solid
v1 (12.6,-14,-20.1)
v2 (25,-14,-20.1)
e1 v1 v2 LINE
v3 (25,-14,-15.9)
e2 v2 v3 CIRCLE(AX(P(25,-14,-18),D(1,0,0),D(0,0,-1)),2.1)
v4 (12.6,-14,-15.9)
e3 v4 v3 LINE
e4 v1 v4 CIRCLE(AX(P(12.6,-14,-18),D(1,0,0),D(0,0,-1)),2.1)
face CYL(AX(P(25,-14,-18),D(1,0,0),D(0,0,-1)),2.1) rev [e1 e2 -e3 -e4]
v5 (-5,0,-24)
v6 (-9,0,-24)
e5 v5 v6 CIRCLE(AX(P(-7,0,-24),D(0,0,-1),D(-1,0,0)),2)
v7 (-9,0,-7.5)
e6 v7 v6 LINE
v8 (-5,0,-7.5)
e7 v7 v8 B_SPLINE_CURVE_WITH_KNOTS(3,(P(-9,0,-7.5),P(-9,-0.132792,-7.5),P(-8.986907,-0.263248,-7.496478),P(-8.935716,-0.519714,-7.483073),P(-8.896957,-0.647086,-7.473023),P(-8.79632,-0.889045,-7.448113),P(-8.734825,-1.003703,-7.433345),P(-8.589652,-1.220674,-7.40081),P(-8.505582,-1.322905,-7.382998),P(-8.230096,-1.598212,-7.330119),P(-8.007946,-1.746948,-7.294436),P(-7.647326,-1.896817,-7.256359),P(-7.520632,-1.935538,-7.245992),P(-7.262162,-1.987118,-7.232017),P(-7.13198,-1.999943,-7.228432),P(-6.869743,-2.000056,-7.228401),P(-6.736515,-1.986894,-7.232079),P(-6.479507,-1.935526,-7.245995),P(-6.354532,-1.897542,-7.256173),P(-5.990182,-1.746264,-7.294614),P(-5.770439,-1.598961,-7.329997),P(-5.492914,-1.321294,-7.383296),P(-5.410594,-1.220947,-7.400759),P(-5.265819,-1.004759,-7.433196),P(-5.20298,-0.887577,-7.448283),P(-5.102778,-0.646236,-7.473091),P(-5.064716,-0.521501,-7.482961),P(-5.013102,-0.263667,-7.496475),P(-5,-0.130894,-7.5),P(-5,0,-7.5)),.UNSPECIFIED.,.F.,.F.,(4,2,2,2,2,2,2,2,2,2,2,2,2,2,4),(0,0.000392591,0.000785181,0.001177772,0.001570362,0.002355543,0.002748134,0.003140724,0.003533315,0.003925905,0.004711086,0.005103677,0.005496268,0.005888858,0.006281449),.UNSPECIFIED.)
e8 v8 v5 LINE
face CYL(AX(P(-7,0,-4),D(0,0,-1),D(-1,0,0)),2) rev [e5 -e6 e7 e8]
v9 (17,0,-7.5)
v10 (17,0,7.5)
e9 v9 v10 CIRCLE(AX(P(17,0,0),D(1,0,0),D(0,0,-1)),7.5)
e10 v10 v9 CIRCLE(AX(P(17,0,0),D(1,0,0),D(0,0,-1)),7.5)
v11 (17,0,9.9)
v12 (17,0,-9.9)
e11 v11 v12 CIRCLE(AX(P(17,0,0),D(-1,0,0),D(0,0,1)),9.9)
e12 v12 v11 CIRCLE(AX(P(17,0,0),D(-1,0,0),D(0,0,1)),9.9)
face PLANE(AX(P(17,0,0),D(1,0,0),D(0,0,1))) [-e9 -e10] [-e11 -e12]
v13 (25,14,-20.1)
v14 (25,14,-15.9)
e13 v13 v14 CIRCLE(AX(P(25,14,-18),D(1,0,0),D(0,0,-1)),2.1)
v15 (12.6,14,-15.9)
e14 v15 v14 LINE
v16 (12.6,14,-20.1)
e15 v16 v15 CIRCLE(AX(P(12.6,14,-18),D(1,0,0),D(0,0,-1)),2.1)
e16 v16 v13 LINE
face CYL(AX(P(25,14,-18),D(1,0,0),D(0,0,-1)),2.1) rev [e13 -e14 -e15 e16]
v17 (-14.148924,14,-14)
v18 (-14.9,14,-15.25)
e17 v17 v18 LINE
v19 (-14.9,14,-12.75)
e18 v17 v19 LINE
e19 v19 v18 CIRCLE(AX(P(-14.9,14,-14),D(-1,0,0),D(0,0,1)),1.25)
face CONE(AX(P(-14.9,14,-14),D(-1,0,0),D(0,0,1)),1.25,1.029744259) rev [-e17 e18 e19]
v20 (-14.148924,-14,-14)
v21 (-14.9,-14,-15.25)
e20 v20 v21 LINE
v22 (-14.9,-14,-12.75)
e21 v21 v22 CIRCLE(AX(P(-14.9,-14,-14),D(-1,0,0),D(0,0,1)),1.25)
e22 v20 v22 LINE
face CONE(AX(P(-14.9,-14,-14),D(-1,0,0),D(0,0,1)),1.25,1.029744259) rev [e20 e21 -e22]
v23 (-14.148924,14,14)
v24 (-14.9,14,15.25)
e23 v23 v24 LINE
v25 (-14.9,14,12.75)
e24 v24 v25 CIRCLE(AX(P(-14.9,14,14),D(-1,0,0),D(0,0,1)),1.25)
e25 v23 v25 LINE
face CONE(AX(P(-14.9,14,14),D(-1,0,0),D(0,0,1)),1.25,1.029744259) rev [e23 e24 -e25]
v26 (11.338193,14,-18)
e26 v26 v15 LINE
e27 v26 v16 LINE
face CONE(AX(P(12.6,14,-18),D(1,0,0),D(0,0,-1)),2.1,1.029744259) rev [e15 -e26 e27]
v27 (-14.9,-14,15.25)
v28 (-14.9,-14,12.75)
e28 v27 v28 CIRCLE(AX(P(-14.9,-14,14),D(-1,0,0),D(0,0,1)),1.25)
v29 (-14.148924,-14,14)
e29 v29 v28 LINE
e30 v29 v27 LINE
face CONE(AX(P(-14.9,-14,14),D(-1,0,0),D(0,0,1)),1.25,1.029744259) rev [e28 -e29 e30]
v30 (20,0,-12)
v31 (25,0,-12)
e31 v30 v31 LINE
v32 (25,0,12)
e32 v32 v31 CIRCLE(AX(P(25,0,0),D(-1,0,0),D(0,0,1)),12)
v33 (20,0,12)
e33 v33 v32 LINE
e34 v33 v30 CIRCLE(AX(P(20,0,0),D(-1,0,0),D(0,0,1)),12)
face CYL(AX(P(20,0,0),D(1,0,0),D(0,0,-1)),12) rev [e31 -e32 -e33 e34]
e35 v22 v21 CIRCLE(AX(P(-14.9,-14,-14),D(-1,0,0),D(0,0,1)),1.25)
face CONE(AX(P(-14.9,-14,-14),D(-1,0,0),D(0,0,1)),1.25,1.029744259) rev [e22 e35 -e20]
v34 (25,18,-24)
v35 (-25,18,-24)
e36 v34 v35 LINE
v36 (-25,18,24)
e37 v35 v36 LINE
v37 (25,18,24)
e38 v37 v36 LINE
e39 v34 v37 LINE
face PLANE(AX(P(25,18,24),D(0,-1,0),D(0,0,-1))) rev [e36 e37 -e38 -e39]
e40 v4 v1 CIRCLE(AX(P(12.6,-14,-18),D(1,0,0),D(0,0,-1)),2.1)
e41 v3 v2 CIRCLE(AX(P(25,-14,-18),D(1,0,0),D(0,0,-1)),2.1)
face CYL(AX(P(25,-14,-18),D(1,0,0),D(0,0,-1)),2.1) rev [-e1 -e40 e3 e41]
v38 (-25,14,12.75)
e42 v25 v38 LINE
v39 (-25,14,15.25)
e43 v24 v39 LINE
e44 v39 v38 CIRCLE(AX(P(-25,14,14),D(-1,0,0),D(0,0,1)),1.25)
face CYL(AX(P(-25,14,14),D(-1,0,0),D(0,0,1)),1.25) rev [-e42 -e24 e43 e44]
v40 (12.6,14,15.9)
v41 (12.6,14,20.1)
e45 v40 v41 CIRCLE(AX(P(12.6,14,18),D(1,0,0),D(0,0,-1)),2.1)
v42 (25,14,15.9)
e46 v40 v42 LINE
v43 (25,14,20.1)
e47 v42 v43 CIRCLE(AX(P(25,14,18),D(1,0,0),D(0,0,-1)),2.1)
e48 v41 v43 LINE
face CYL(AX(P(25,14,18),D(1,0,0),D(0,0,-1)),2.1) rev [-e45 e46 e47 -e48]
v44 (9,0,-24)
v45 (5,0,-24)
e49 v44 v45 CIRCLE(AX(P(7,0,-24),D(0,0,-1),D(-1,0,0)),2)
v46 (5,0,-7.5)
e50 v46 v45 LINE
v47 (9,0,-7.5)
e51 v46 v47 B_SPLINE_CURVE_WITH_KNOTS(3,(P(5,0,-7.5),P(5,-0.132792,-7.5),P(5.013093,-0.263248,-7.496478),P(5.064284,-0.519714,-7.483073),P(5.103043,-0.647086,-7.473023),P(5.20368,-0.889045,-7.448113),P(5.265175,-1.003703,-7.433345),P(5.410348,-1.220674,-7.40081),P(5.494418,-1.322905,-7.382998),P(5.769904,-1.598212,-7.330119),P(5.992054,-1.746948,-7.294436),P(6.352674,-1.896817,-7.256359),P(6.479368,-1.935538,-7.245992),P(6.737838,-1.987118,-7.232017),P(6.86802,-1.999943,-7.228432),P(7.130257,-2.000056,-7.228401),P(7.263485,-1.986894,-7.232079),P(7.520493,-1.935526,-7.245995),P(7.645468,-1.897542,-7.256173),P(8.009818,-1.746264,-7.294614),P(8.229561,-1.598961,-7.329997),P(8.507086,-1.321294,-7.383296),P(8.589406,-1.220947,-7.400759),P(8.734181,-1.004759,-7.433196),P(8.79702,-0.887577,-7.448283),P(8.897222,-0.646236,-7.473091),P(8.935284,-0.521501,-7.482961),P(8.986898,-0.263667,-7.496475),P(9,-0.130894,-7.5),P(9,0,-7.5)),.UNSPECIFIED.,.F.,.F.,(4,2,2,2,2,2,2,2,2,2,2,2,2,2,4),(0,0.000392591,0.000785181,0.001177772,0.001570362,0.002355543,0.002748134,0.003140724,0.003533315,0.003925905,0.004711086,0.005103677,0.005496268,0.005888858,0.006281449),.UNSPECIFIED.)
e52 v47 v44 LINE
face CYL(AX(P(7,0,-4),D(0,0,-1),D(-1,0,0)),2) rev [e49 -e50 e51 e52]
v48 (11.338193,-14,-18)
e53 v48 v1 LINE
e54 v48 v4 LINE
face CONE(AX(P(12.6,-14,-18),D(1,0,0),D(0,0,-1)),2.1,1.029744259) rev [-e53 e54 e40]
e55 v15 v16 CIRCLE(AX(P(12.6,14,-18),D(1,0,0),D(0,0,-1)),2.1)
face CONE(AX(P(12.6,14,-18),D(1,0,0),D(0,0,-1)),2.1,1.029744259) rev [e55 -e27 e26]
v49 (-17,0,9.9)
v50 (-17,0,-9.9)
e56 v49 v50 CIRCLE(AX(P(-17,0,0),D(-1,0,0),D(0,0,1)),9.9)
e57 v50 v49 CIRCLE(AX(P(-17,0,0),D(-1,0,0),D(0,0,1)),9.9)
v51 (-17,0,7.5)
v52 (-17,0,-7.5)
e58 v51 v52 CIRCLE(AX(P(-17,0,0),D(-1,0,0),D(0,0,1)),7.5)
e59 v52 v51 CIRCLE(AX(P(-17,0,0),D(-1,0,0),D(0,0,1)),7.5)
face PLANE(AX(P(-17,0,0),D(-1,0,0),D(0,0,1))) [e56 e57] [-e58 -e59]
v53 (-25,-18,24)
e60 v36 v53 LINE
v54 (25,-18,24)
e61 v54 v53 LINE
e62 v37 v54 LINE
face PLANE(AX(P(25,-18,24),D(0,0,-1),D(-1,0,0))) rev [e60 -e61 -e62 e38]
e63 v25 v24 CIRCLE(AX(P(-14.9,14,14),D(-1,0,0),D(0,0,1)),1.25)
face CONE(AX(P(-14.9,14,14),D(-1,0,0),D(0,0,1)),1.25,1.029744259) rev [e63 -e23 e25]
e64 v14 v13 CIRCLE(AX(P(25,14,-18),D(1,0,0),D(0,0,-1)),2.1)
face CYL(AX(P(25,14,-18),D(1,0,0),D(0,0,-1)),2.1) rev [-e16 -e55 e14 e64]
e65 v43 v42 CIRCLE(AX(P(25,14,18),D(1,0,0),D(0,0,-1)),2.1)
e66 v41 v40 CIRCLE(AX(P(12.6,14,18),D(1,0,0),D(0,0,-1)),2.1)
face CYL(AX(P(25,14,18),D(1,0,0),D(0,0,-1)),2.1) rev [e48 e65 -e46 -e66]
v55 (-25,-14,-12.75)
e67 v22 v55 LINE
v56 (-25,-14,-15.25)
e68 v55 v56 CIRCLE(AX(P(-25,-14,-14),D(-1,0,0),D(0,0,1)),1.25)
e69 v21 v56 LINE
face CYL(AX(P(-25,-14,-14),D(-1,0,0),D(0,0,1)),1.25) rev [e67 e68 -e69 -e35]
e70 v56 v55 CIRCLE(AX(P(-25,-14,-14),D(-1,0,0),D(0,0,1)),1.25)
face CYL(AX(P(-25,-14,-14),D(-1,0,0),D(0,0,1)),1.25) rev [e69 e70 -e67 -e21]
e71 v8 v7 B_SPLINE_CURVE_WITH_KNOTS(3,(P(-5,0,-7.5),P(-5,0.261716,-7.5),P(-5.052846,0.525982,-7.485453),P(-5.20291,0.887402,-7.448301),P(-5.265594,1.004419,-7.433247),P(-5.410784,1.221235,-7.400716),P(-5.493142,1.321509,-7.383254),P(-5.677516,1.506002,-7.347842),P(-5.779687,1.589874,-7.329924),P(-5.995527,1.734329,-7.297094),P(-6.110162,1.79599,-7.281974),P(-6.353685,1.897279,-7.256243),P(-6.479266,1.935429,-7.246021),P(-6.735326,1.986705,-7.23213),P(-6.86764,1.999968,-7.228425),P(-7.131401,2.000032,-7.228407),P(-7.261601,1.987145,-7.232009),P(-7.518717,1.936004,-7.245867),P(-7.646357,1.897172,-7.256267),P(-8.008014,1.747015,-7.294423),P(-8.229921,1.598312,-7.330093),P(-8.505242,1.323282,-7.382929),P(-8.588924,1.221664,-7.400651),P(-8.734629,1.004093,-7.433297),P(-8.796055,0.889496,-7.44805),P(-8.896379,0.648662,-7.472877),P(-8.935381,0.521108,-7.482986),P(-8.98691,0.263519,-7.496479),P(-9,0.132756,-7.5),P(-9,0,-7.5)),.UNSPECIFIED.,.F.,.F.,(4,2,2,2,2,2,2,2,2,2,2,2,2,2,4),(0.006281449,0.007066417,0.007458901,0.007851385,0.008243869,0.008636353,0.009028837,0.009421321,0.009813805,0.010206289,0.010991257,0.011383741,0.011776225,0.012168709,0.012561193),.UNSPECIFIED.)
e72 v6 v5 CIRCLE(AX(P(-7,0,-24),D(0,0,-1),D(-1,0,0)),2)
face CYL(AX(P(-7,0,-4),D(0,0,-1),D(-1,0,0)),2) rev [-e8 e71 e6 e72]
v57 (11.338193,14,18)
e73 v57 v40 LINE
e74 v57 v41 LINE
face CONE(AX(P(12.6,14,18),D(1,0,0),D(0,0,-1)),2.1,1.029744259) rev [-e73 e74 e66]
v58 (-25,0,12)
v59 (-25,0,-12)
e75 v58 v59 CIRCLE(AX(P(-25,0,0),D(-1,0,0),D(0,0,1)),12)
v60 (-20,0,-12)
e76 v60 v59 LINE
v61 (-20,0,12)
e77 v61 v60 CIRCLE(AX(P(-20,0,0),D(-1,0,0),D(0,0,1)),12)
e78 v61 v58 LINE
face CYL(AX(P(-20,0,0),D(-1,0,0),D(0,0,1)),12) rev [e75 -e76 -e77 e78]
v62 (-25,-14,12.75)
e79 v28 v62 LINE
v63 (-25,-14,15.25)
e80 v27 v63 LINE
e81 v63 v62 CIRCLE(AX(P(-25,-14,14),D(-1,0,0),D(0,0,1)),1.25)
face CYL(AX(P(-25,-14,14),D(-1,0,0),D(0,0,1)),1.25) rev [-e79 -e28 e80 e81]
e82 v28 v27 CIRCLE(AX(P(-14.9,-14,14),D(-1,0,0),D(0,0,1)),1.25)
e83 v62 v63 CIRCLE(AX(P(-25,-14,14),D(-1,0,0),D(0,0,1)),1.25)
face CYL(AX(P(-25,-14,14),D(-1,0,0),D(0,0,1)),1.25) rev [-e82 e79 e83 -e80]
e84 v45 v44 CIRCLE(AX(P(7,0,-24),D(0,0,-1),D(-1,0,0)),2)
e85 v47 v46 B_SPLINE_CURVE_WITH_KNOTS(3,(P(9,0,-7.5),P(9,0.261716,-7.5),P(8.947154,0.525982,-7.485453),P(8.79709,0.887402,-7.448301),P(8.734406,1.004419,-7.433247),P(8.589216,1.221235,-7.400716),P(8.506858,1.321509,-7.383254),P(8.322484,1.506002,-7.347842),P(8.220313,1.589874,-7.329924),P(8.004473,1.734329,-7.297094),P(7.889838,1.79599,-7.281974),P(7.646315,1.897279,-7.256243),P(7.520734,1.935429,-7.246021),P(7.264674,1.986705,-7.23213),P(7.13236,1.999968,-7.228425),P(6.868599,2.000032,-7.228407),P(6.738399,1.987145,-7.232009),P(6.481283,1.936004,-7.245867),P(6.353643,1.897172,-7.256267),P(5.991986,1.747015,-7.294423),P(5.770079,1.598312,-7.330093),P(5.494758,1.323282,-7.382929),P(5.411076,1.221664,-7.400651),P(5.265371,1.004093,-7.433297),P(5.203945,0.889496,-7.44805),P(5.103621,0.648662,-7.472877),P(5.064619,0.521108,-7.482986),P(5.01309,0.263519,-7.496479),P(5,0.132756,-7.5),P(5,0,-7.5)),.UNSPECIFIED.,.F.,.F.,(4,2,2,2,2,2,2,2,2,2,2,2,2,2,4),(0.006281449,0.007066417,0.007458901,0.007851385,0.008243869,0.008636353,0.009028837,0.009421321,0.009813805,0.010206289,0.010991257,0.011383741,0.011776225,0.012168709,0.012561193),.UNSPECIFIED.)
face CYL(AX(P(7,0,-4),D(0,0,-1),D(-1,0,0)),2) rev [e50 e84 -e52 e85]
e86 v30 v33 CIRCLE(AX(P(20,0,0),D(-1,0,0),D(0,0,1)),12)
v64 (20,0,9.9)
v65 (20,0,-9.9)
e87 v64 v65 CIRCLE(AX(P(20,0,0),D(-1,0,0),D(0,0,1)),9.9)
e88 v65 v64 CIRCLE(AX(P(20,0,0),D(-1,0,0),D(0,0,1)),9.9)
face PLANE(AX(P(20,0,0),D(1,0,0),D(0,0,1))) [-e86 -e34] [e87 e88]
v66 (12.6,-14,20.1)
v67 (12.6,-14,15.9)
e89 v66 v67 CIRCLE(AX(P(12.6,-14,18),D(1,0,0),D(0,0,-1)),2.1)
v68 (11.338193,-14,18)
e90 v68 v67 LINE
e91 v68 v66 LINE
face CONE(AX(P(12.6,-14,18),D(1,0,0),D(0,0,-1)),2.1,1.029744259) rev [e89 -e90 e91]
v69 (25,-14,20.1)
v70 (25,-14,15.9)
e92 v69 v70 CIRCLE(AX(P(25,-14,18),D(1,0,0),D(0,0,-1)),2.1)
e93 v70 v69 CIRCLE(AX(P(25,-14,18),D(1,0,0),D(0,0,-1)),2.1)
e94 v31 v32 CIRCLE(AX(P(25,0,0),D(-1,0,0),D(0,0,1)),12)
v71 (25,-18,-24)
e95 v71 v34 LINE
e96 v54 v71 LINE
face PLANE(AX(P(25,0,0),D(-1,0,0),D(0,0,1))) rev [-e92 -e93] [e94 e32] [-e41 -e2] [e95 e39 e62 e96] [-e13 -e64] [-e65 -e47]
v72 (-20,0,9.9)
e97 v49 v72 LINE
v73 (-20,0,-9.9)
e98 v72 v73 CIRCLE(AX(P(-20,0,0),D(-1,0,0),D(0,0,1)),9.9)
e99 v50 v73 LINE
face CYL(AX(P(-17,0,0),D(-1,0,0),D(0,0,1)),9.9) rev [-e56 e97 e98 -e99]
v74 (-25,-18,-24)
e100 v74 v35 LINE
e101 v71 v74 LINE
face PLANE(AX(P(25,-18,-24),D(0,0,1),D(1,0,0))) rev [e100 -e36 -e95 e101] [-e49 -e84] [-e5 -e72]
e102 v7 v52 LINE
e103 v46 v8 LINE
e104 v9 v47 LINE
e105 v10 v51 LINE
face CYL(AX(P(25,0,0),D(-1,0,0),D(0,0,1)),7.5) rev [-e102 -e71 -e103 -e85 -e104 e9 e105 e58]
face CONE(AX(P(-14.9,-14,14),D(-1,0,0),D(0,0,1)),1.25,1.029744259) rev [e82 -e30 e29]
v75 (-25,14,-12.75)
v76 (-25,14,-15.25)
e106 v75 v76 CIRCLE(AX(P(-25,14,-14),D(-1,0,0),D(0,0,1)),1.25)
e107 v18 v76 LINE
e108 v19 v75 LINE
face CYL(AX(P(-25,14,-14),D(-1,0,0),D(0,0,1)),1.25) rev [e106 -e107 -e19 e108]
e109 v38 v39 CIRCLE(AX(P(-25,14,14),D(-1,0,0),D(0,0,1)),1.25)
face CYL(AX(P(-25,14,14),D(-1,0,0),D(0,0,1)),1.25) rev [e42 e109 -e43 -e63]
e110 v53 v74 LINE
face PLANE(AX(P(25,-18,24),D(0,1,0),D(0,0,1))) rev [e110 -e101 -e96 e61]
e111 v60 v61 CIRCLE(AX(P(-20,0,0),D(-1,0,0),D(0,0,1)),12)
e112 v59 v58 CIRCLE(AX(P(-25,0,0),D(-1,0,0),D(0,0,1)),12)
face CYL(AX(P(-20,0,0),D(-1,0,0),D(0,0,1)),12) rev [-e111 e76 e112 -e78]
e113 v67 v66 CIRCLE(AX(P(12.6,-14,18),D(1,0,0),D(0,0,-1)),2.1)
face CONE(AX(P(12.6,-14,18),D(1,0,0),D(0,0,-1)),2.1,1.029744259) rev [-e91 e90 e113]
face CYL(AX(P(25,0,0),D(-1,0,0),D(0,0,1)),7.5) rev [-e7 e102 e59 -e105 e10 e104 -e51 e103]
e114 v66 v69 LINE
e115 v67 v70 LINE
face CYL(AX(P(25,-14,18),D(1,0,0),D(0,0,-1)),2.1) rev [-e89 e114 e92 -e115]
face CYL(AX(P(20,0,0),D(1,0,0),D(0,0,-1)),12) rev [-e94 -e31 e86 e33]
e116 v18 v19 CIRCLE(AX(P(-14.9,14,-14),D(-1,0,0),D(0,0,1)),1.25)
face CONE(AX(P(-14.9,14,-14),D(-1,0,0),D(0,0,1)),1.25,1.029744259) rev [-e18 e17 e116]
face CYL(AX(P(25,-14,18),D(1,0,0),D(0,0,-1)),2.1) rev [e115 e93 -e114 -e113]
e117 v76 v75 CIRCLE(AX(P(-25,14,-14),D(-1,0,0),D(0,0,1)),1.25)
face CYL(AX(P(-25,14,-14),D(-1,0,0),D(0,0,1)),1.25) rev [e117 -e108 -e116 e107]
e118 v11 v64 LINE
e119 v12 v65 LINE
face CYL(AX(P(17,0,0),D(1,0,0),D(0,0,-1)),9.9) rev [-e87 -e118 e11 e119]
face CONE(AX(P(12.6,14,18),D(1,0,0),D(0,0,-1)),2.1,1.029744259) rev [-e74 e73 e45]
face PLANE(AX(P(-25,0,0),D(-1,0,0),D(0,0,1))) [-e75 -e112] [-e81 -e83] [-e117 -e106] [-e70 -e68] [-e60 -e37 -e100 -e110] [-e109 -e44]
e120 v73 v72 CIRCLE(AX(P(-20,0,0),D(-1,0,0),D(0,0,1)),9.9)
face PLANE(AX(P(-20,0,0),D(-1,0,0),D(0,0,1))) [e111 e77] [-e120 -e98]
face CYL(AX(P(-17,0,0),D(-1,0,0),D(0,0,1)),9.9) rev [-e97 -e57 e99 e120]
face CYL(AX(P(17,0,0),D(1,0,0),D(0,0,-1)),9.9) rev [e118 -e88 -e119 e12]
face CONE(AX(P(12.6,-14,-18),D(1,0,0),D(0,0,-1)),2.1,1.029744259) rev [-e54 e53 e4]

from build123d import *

# Parameters (mm, degrees)
SKETCH1_W             = 48
SKETCH1_H             = 36
SKETCH1_R             = 7.5
BOSS_EXTRUDE1_DEPTH   = 25
SKETCH2_R             = 12
CUT_EXTRUDE1_DEPTH    = 5
SKETCH3_R             = 9.9
CUT_EXTRUDE2_DEPTH    = 3
SKETCH5_R             = 2
CUT_EXTRUDE3_DEPTH    = 20
M5_TAPPED_HOLE1_D     = 4.2
M5_TAPPED_HOLE1_DEPTH = 12.4
M5_TAPPED_HOLE1_TIP   = 1.2618073
M3_TAPPED_HOLE1_D     = 2.5
M3_TAPPED_HOLE1_DEPTH = 10.1
M3_TAPPED_HOLE1_TIP   = 0.751075774


with BuildPart() as part:
    # Sketch1 → Boss-Extrude1 (new, symmetric)
    with BuildSketch(Plane(origin=(0, 0, 0), x_dir=(0, 0, -1), z_dir=(1, 0, 0))):
        Rectangle(SKETCH1_W, SKETCH1_H)
        Circle(SKETCH1_R, mode=Mode.SUBTRACT)
    extrude(amount=BOSS_EXTRUDE1_DEPTH, both=True)

    # Sketch2 → Cut-Extrude1 (cut)
    with BuildSketch(Plane.ZY.offset(25)):
        Circle(SKETCH2_R)
    cut_extrude1 = extrude(amount=-CUT_EXTRUDE1_DEPTH, mode=Mode.SUBTRACT)

    # Sketch3 → Cut-Extrude2 (cut)
    with BuildSketch(Plane.ZY.offset(20)):
        Circle(SKETCH3_R)
    cut_extrude2 = extrude(amount=-CUT_EXTRUDE2_DEPTH, mode=Mode.SUBTRACT)

    # Mirror4: Cut-Extrude1, Cut-Extrude2 across plane
    add(cut_extrude1.mirror(Plane(origin=(0, 0, 0), x_dir=(0, 0, 1), z_dir=(1, 0, 0))), mode=Mode.SUBTRACT)
    add(cut_extrude2.mirror(Plane(origin=(0, 0, 0), x_dir=(0, 0, 1), z_dir=(1, 0, 0))), mode=Mode.SUBTRACT)

    # Sketch5 → Cut-Extrude3 (cut)
    with BuildSketch(Plane(origin=(0, 0, -24), x_dir=(-1, 0, 0), z_dir=(0, 0, -1))):
        with Locations((7, 0)):
            Circle(SKETCH5_R)
        with Locations((-7, 0)):
            Circle(SKETCH5_R)
    extrude(amount=-CUT_EXTRUDE3_DEPTH, mode=Mode.SUBTRACT)

    # M5 Tapped Hole1
    with Locations(Plane(origin=(25, 0, 0), x_dir=(0, 0, -1), z_dir=(1, 0, 0))):
        with Locations((-18, 14), (18, 14), (-18, -14), (18, -14)):
            Hole(M5_TAPPED_HOLE1_D / 2, depth=M5_TAPPED_HOLE1_DEPTH)
            with Locations((0, 0, -(M5_TAPPED_HOLE1_DEPTH + M5_TAPPED_HOLE1_TIP / 2))):  # 118° drill point
                Cone(0, M5_TAPPED_HOLE1_D / 2, M5_TAPPED_HOLE1_TIP, mode=Mode.SUBTRACT)

    # M3 Tapped Hole1
    with Locations(Plane.ZY.offset(25)):
        with Locations((-14, 14), (-14, -14), (14, 14), (14, -14)):
            Hole(M3_TAPPED_HOLE1_D / 2, depth=M3_TAPPED_HOLE1_DEPTH)
            with Locations((0, 0, -(M3_TAPPED_HOLE1_DEPTH + M3_TAPPED_HOLE1_TIP / 2))):  # 118° drill point
                Cone(0, M3_TAPPED_HOLE1_D / 2, M3_TAPPED_HOLE1_TIP, mode=Mode.SUBTRACT)


solid = part.part
